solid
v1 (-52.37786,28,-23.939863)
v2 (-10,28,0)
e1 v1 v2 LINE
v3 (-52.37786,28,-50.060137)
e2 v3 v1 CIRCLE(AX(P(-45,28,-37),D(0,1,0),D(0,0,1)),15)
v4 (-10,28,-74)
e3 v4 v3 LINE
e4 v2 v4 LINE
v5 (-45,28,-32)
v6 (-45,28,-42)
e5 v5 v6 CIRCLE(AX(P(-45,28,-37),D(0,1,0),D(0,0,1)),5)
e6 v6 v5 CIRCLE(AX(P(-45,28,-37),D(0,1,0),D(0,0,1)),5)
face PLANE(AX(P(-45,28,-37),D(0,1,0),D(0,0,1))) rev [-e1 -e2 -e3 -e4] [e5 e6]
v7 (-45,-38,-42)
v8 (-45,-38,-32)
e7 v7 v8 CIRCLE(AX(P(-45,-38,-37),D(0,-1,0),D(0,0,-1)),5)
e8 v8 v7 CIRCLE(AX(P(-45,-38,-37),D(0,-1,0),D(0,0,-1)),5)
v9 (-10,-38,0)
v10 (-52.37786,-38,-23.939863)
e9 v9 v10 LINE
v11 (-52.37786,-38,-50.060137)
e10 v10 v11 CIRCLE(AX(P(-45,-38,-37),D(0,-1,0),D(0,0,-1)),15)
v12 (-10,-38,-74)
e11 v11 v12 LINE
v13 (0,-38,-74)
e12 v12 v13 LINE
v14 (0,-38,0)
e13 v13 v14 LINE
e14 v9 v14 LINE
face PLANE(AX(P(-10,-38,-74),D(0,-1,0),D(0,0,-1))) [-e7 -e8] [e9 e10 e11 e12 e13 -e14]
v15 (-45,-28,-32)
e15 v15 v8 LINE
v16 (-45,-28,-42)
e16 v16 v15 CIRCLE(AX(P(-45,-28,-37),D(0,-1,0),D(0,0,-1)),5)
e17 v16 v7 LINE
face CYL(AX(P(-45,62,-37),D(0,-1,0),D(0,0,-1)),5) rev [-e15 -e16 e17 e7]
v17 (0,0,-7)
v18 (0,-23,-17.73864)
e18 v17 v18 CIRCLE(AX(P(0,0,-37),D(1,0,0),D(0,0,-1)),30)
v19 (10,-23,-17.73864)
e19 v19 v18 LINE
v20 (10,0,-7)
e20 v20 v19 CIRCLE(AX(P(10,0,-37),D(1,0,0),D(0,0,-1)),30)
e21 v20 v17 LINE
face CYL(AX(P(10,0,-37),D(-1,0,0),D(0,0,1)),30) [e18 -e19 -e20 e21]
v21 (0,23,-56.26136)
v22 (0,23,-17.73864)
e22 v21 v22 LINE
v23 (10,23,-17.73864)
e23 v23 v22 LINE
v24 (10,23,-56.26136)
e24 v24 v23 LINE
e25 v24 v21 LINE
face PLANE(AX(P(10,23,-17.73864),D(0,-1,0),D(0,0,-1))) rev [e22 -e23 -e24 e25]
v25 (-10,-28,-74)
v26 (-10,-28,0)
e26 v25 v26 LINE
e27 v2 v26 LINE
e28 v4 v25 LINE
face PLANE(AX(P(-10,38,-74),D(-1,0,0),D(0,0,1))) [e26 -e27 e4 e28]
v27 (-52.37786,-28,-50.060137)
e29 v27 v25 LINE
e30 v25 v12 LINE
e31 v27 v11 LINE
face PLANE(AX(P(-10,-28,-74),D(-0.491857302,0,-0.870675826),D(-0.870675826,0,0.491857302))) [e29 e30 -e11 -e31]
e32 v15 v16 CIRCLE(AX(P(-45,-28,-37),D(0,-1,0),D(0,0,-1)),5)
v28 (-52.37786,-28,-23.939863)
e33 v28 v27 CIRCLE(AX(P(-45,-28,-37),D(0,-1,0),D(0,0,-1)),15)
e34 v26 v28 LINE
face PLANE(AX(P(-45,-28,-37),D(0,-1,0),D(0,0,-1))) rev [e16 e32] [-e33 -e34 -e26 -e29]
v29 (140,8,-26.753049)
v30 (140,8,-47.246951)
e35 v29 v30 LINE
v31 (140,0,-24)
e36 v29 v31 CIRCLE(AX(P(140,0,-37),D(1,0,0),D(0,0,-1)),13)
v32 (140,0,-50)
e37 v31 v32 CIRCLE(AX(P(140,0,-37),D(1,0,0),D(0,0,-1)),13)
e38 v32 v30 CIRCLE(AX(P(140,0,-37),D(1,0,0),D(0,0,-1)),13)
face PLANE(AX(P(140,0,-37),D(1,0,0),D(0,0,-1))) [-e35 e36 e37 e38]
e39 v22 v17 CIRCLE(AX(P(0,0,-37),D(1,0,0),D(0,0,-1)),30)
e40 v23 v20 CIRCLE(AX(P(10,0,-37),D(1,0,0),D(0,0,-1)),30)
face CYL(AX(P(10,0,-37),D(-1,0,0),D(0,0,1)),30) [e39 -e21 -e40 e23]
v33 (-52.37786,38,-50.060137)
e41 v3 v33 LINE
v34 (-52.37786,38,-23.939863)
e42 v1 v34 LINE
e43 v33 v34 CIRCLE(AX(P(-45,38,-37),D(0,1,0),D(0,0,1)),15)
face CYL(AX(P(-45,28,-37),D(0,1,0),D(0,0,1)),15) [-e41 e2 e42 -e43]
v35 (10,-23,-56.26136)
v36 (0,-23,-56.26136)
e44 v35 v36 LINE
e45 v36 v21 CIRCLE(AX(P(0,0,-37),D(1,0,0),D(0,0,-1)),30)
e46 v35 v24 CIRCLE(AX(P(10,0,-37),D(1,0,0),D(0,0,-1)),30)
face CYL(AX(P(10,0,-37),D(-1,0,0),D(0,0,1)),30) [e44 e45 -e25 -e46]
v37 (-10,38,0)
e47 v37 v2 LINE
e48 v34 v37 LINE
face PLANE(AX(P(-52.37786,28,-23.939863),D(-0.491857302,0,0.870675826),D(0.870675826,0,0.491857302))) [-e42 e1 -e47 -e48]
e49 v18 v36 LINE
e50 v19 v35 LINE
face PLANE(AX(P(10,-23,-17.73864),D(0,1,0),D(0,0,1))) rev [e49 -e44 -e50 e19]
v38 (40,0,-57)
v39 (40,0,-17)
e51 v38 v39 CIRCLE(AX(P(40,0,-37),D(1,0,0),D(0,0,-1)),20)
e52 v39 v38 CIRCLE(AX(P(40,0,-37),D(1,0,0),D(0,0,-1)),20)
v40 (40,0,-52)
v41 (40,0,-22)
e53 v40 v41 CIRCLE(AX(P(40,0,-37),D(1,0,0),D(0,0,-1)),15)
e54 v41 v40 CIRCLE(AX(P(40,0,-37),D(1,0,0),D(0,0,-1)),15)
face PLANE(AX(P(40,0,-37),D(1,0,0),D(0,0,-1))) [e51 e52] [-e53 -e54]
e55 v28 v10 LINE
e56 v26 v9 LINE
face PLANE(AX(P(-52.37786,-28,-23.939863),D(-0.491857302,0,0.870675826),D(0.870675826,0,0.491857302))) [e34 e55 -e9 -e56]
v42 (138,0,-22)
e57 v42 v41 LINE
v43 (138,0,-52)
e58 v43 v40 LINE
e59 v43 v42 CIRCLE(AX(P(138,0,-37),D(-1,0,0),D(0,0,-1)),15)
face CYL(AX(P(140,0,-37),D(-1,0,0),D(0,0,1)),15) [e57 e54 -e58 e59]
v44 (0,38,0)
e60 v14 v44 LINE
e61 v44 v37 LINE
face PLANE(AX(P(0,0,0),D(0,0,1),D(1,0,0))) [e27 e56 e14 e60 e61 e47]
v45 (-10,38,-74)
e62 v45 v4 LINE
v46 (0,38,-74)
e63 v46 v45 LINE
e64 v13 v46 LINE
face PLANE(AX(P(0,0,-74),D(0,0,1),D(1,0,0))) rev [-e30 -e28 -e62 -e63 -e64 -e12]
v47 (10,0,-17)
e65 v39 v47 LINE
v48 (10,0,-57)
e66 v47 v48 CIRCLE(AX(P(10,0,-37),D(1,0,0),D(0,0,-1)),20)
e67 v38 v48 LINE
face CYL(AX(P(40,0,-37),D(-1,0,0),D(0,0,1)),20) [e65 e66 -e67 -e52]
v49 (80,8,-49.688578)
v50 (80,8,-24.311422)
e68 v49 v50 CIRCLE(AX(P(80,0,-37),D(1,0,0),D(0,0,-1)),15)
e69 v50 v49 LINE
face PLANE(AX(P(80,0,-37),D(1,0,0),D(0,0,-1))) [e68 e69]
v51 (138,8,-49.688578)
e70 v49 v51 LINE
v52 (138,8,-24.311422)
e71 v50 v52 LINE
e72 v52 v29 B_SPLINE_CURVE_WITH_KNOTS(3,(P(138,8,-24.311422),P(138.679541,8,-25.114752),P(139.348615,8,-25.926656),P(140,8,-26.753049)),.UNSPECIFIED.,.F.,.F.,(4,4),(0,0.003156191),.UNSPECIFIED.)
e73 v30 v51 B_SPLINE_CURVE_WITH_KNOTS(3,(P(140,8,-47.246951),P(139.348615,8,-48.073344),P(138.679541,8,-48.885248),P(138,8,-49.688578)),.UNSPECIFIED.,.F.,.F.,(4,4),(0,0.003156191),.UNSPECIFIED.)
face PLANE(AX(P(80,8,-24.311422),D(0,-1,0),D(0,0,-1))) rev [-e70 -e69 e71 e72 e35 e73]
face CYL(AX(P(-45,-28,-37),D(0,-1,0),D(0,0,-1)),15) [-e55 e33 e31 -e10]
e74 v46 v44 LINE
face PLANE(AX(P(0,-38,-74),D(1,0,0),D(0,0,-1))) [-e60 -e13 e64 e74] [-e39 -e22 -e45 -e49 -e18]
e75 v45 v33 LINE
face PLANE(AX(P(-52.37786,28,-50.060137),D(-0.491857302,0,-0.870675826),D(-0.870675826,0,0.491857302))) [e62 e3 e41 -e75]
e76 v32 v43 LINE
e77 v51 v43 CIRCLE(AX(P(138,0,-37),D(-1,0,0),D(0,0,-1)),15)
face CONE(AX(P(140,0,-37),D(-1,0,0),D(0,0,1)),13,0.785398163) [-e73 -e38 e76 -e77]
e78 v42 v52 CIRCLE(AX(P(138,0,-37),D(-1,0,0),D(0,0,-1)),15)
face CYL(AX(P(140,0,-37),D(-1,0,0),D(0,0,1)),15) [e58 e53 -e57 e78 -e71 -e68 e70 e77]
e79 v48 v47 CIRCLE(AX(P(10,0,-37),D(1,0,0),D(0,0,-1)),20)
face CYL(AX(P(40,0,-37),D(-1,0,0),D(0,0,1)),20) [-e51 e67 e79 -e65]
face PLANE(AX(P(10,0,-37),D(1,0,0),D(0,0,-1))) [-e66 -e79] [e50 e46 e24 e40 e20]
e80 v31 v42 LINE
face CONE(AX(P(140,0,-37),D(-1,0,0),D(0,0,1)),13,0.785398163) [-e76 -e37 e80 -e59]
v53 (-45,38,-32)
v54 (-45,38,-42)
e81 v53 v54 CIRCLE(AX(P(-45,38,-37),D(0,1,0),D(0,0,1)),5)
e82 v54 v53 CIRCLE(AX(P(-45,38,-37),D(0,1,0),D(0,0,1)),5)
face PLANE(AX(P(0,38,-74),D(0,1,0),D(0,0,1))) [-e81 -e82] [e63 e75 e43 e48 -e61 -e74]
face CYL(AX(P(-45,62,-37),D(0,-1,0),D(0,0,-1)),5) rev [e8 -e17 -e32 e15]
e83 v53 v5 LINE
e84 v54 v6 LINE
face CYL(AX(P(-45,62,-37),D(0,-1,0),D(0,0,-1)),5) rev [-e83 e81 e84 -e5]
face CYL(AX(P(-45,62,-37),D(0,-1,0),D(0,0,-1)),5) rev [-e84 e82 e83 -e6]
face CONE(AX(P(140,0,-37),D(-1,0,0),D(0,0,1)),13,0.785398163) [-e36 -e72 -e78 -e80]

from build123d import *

# Parameters (mm, degrees)
BASE_PLATE_SKETCH_W         = 10
BASE_PLATE_SKETCH_H         = 76
BASE_PLATE_DEPTH            = 74
FORK_EAR_1_DEPTH            = 10
FORK_START                  = -10
FORK_EAR_2_DEPTH            = 10
PIVOT_PIN_HOLE_SKETCH_R     = 5
PIVOT_PIN_HOLE_10_DEPTH     = 100
HEX_COLLAR_DEPTH            = 10
SHOULDER_40_SKETCH_R        = 20
SHOULDER_40_DEPTH           = 30
SHAFT_30_SKETCH_R           = 15
SHAFT_30_DEPTH              = 100
SHAFT_START                 = -60
SHAFT_FLAT_DEPTH            = 60
SHAFT_END_CHAMFER_2X45_SIZE = 2


with BuildPart() as part:
    # Base Plate Sketch → Base Plate (new body)
    with BuildSketch(Plane.XY):
        with Locations((-5, 0)):
            Rectangle(BASE_PLATE_SKETCH_W, BASE_PLATE_SKETCH_H)
    extrude(amount=-BASE_PLATE_DEPTH)

    # Fork Ear 1 Sketch → Fork Ear 1 (add)
    with BuildSketch(Plane(origin=(0, 38, 0), x_dir=(1, 0, 0), z_dir=(0, 1, 0))):
        with BuildLine():
            Line((-10, 74), (-10, 0))
            Line((-10, 0), (-52.377859531, 23.939862606))
            ThreePointArc((-52.377859531, 23.939862606), (-60, 37), (-52.377859531, 50.060137394))
            Line((-52.377859531, 50.060137394), (-10, 74))
        make_face()
    extrude(amount=-FORK_EAR_1_DEPTH)

    # Fork Ear 2 Sketch → Fork Ear 2 (add)
    with BuildSketch(Plane.XZ.offset(38).offset(FORK_START)):
        with BuildLine():
            Line((-52.377859531, -23.939862606), (-10, 0))
            Line((-10, 0), (-10, -74))
            Line((-10, -74), (-52.377859531, -50.060137394))
            ThreePointArc((-52.377859531, -50.060137394), (-60, -37), (-52.377859531, -23.939862606))
        make_face()
    extrude(amount=FORK_EAR_2_DEPTH)

    # Pivot Pin Hole Sketch → Pivot Pin Hole Ø10 (cut)
    with BuildSketch(Plane.XZ.offset(38)):
        with Locations(Location((-45, -37, 0), (0, 0, 270))):
            Circle(PIVOT_PIN_HOLE_SKETCH_R)
    extrude(amount=-PIVOT_PIN_HOLE_10_DEPTH, mode=Mode.SUBTRACT)

    # Hex Collar Sketch → Hex Collar (add)
    with BuildSketch(Plane(origin=(0, 0, 0), x_dir=(0, 0, -1), z_dir=(1, 0, 0))):
        with BuildLine():
            Line((17.738639716, 23), (56.261360284, 23))
            ThreePointArc((56.261360284, 23), (67, 0), (56.261360284, -23))
            Line((56.261360284, -23), (17.738639716, -23))
            ThreePointArc((17.738639716, -23), (7, 0), (17.738639716, 23))
        make_face()
    extrude(amount=HEX_COLLAR_DEPTH)

    # Shoulder Ø40 Sketch → Shoulder Ø40 (add)
    with BuildSketch(Plane(origin=(10, 0, 0), x_dir=(0, 0, -1), z_dir=(1, 0, 0))):
        with Locations((37, 0)):
            Circle(SHOULDER_40_SKETCH_R)
    extrude(amount=SHOULDER_40_DEPTH)

    # Shaft Ø30 Sketch → Shaft Ø30 (add)
    with BuildSketch(Plane(origin=(40, 0, 0), x_dir=(0, 0, -1), z_dir=(1, 0, 0))):
        with Locations((37, 0)):
            Circle(SHAFT_30_SKETCH_R)
    extrude(amount=SHAFT_30_DEPTH)

    # Shaft Flat Sketch → Shaft Flat (cut)
    with BuildSketch(Plane(origin=(140, 0, 0), x_dir=(0, 0, -1), z_dir=(1, 0, 0)).offset(SHAFT_START)):
        with BuildLine():
            Line((24.31142246, 8), (49.68857754, 8))
            ThreePointArc((49.68857754, 8), (37, 15), (24.31142246, 8))
        make_face()
    extrude(amount=SHAFT_FLAT_DEPTH, mode=Mode.SUBTRACT)

    # Shaft End Chamfer 2x45°
    shaft_end_chamfer_2x45_edges = [part.edges().sort_by_distance(p)[0] for p in [
        (140, -14.410563193, -32.836387572),
    ]]
    chamfer(shaft_end_chamfer_2x45_edges, length=SHAFT_END_CHAMFER_2X45_SIZE)


solid = part.part
